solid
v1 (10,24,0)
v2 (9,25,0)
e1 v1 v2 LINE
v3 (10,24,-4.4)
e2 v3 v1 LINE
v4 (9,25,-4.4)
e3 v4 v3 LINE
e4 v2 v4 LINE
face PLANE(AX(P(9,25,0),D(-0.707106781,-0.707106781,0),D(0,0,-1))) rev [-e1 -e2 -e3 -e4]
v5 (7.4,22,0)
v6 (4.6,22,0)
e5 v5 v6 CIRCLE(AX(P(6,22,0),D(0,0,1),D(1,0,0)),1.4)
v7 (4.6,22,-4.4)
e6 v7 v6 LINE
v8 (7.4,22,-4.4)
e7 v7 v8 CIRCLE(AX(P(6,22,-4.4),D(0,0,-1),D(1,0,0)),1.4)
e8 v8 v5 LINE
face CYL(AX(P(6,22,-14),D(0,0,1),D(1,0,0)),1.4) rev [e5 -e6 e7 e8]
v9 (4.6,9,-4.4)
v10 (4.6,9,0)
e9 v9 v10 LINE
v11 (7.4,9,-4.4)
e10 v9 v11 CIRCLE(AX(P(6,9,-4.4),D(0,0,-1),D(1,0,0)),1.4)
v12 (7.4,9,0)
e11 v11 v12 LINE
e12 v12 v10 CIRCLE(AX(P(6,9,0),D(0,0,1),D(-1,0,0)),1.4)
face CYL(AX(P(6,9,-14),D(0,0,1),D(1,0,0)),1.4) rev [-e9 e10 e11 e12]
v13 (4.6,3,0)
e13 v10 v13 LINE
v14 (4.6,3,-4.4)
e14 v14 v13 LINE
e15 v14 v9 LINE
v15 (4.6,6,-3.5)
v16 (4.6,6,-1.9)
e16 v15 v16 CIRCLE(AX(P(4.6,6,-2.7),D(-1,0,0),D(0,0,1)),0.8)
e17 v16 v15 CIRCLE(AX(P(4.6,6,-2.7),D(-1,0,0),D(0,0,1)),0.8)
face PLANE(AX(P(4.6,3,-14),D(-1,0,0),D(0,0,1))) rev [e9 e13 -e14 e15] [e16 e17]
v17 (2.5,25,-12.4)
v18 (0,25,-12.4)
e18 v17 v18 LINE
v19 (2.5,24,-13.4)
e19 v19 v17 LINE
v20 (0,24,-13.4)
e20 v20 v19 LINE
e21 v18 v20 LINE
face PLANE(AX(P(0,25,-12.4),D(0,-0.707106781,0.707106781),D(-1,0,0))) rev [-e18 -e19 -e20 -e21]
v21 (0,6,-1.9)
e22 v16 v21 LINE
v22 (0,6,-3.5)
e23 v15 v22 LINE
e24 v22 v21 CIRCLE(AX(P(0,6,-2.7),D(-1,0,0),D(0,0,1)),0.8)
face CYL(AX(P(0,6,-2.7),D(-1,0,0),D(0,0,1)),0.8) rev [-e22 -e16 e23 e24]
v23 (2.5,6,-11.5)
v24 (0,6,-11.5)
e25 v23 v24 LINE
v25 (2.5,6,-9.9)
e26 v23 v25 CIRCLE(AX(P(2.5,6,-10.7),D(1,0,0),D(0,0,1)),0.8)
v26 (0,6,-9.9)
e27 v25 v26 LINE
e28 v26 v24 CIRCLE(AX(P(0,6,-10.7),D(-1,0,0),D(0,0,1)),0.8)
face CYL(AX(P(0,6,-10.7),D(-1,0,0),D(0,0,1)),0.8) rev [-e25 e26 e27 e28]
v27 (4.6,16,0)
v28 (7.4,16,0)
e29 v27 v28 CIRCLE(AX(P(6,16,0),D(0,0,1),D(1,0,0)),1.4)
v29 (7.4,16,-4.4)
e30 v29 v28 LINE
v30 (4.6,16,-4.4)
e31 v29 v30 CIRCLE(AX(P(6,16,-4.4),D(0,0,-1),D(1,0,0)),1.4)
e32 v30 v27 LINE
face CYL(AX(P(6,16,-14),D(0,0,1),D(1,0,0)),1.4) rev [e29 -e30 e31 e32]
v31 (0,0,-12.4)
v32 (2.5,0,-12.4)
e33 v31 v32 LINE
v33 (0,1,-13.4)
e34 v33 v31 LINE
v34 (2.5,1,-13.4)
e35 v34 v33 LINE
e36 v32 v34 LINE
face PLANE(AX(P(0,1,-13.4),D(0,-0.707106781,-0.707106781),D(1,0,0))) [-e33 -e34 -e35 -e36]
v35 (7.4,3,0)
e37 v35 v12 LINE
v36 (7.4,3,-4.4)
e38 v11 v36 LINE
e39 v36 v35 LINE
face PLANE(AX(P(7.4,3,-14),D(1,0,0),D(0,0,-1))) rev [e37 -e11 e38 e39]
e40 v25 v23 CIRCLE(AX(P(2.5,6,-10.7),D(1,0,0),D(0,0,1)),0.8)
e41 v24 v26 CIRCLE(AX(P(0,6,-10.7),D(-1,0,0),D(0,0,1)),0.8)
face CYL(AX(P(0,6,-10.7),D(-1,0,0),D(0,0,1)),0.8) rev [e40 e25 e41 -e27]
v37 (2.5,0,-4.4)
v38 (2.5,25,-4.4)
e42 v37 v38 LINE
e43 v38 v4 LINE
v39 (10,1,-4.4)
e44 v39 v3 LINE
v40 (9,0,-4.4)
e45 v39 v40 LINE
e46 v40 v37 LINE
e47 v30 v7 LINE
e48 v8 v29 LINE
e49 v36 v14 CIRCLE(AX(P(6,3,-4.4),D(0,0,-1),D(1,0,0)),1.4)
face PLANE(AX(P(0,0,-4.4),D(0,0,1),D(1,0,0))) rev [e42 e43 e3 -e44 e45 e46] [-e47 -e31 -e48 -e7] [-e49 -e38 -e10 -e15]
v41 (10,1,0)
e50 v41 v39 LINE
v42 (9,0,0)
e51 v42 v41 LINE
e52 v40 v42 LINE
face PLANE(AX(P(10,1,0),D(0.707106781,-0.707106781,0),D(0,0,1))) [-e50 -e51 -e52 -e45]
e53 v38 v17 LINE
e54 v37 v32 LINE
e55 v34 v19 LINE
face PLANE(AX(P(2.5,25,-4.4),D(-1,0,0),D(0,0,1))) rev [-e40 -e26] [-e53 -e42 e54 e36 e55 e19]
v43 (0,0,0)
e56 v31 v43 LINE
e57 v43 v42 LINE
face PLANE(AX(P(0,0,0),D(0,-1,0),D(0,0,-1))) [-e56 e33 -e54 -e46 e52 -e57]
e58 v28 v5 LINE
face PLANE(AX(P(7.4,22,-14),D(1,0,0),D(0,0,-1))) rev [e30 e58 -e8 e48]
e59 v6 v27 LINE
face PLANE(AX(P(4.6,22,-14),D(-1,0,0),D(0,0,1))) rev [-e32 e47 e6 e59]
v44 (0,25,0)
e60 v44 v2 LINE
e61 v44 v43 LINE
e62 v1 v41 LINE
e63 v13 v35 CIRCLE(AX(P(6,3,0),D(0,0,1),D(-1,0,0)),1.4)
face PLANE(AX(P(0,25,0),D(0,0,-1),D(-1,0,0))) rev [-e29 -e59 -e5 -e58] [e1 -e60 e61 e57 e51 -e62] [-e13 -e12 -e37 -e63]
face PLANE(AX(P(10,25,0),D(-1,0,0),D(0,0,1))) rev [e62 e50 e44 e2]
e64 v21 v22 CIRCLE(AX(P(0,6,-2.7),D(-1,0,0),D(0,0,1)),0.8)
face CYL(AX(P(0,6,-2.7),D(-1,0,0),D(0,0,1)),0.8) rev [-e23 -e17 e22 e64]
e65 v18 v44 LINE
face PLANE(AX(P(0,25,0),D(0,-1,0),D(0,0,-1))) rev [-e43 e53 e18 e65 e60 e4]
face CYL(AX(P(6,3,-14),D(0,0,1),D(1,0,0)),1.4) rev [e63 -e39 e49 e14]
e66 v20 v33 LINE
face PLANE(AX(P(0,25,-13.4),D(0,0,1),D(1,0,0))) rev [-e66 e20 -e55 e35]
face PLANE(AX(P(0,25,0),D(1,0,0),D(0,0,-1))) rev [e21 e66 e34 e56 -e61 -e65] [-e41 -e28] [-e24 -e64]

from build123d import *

# Parameters (mm, degrees)
SKETCH1_W             = 10
SKETCH1_H             = 13.4
BOSS_EXTRUDE1_DEPTH   = 25
CUT_EXTRUDE2_DEPTH    = 14
M2_TAPPED_HOLE1_D     = 1.6
M2_TAPPED_HOLE1_DEPTH = 5.2
M2_TAPPED_HOLE1_TIP   = 0.480688495
SKETCH7_W             = 9.563839575
SKETCH7_H             = 25
CUT_EXTRUDE3_DEPTH    = 9
CHAMFER1_SIZE         = 1


with BuildPart() as part:
    # Sketch1 → Boss-Extrude1 (new body)
    with BuildSketch(Plane(origin=(0, 0, 0), x_dir=(1, 0, 0), z_dir=(0, 1, 0))):
        with Locations((5, 6.7)):
            Rectangle(SKETCH1_W, SKETCH1_H)
    extrude(amount=BOSS_EXTRUDE1_DEPTH)

    # Q → Cut-Extrude2 (cut)
    with BuildSketch(Plane.XY):
        with BuildLine():
            Line((7.4, 22), (7.4, 16))
            ThreePointArc((7.4, 16), (6, 14.6), (4.6, 16))
            Line((4.6, 16), (4.6, 22))
            ThreePointArc((4.6, 22), (6, 23.4), (7.4, 22))
        make_face()
        with BuildLine():
            Line((7.4, 3), (7.4, 9))
            ThreePointArc((7.4, 9), (6, 10.4), (4.6, 9))
            Line((4.6, 9), (4.6, 3))
            ThreePointArc((4.6, 3), (6, 1.6), (7.4, 3))
        make_face()
    extrude(amount=-CUT_EXTRUDE2_DEPTH, mode=Mode.SUBTRACT)

    # M2 Tapped Hole1
    with Locations(Plane.ZY):
        with Locations((-10.7, 6), (-2.7, 6)):
            Hole(M2_TAPPED_HOLE1_D / 2, depth=M2_TAPPED_HOLE1_DEPTH)
            with Locations((0, 0, -(M2_TAPPED_HOLE1_DEPTH + M2_TAPPED_HOLE1_TIP / 2))):  # 118° drill point
                Cone(0, M2_TAPPED_HOLE1_D / 2, M2_TAPPED_HOLE1_TIP, mode=Mode.SUBTRACT)

    # Sketch7 → Cut-Extrude3 (cut)
    with BuildSketch(Plane(origin=(0, 0, -13.4), x_dir=(-1, 0, 0), z_dir=(0, 0, -1))):
        with Locations((-7.281919788, 12.5)):
            Rectangle(SKETCH7_W, SKETCH7_H)
    extrude(amount=-CUT_EXTRUDE3_DEPTH, mode=Mode.SUBTRACT)

    # Chamfer1
    chamfer1_edges = [part.edges().sort_by_distance(p)[0] for p in [
        (10, 25, -2.2),
        (10, 0, -2.2),
        (1.25, 0, -13.4),
        (1.25, 25, -13.4),
    ]]
    chamfer(chamfer1_edges, length=CHAMFER1_SIZE)


solid = part.part
